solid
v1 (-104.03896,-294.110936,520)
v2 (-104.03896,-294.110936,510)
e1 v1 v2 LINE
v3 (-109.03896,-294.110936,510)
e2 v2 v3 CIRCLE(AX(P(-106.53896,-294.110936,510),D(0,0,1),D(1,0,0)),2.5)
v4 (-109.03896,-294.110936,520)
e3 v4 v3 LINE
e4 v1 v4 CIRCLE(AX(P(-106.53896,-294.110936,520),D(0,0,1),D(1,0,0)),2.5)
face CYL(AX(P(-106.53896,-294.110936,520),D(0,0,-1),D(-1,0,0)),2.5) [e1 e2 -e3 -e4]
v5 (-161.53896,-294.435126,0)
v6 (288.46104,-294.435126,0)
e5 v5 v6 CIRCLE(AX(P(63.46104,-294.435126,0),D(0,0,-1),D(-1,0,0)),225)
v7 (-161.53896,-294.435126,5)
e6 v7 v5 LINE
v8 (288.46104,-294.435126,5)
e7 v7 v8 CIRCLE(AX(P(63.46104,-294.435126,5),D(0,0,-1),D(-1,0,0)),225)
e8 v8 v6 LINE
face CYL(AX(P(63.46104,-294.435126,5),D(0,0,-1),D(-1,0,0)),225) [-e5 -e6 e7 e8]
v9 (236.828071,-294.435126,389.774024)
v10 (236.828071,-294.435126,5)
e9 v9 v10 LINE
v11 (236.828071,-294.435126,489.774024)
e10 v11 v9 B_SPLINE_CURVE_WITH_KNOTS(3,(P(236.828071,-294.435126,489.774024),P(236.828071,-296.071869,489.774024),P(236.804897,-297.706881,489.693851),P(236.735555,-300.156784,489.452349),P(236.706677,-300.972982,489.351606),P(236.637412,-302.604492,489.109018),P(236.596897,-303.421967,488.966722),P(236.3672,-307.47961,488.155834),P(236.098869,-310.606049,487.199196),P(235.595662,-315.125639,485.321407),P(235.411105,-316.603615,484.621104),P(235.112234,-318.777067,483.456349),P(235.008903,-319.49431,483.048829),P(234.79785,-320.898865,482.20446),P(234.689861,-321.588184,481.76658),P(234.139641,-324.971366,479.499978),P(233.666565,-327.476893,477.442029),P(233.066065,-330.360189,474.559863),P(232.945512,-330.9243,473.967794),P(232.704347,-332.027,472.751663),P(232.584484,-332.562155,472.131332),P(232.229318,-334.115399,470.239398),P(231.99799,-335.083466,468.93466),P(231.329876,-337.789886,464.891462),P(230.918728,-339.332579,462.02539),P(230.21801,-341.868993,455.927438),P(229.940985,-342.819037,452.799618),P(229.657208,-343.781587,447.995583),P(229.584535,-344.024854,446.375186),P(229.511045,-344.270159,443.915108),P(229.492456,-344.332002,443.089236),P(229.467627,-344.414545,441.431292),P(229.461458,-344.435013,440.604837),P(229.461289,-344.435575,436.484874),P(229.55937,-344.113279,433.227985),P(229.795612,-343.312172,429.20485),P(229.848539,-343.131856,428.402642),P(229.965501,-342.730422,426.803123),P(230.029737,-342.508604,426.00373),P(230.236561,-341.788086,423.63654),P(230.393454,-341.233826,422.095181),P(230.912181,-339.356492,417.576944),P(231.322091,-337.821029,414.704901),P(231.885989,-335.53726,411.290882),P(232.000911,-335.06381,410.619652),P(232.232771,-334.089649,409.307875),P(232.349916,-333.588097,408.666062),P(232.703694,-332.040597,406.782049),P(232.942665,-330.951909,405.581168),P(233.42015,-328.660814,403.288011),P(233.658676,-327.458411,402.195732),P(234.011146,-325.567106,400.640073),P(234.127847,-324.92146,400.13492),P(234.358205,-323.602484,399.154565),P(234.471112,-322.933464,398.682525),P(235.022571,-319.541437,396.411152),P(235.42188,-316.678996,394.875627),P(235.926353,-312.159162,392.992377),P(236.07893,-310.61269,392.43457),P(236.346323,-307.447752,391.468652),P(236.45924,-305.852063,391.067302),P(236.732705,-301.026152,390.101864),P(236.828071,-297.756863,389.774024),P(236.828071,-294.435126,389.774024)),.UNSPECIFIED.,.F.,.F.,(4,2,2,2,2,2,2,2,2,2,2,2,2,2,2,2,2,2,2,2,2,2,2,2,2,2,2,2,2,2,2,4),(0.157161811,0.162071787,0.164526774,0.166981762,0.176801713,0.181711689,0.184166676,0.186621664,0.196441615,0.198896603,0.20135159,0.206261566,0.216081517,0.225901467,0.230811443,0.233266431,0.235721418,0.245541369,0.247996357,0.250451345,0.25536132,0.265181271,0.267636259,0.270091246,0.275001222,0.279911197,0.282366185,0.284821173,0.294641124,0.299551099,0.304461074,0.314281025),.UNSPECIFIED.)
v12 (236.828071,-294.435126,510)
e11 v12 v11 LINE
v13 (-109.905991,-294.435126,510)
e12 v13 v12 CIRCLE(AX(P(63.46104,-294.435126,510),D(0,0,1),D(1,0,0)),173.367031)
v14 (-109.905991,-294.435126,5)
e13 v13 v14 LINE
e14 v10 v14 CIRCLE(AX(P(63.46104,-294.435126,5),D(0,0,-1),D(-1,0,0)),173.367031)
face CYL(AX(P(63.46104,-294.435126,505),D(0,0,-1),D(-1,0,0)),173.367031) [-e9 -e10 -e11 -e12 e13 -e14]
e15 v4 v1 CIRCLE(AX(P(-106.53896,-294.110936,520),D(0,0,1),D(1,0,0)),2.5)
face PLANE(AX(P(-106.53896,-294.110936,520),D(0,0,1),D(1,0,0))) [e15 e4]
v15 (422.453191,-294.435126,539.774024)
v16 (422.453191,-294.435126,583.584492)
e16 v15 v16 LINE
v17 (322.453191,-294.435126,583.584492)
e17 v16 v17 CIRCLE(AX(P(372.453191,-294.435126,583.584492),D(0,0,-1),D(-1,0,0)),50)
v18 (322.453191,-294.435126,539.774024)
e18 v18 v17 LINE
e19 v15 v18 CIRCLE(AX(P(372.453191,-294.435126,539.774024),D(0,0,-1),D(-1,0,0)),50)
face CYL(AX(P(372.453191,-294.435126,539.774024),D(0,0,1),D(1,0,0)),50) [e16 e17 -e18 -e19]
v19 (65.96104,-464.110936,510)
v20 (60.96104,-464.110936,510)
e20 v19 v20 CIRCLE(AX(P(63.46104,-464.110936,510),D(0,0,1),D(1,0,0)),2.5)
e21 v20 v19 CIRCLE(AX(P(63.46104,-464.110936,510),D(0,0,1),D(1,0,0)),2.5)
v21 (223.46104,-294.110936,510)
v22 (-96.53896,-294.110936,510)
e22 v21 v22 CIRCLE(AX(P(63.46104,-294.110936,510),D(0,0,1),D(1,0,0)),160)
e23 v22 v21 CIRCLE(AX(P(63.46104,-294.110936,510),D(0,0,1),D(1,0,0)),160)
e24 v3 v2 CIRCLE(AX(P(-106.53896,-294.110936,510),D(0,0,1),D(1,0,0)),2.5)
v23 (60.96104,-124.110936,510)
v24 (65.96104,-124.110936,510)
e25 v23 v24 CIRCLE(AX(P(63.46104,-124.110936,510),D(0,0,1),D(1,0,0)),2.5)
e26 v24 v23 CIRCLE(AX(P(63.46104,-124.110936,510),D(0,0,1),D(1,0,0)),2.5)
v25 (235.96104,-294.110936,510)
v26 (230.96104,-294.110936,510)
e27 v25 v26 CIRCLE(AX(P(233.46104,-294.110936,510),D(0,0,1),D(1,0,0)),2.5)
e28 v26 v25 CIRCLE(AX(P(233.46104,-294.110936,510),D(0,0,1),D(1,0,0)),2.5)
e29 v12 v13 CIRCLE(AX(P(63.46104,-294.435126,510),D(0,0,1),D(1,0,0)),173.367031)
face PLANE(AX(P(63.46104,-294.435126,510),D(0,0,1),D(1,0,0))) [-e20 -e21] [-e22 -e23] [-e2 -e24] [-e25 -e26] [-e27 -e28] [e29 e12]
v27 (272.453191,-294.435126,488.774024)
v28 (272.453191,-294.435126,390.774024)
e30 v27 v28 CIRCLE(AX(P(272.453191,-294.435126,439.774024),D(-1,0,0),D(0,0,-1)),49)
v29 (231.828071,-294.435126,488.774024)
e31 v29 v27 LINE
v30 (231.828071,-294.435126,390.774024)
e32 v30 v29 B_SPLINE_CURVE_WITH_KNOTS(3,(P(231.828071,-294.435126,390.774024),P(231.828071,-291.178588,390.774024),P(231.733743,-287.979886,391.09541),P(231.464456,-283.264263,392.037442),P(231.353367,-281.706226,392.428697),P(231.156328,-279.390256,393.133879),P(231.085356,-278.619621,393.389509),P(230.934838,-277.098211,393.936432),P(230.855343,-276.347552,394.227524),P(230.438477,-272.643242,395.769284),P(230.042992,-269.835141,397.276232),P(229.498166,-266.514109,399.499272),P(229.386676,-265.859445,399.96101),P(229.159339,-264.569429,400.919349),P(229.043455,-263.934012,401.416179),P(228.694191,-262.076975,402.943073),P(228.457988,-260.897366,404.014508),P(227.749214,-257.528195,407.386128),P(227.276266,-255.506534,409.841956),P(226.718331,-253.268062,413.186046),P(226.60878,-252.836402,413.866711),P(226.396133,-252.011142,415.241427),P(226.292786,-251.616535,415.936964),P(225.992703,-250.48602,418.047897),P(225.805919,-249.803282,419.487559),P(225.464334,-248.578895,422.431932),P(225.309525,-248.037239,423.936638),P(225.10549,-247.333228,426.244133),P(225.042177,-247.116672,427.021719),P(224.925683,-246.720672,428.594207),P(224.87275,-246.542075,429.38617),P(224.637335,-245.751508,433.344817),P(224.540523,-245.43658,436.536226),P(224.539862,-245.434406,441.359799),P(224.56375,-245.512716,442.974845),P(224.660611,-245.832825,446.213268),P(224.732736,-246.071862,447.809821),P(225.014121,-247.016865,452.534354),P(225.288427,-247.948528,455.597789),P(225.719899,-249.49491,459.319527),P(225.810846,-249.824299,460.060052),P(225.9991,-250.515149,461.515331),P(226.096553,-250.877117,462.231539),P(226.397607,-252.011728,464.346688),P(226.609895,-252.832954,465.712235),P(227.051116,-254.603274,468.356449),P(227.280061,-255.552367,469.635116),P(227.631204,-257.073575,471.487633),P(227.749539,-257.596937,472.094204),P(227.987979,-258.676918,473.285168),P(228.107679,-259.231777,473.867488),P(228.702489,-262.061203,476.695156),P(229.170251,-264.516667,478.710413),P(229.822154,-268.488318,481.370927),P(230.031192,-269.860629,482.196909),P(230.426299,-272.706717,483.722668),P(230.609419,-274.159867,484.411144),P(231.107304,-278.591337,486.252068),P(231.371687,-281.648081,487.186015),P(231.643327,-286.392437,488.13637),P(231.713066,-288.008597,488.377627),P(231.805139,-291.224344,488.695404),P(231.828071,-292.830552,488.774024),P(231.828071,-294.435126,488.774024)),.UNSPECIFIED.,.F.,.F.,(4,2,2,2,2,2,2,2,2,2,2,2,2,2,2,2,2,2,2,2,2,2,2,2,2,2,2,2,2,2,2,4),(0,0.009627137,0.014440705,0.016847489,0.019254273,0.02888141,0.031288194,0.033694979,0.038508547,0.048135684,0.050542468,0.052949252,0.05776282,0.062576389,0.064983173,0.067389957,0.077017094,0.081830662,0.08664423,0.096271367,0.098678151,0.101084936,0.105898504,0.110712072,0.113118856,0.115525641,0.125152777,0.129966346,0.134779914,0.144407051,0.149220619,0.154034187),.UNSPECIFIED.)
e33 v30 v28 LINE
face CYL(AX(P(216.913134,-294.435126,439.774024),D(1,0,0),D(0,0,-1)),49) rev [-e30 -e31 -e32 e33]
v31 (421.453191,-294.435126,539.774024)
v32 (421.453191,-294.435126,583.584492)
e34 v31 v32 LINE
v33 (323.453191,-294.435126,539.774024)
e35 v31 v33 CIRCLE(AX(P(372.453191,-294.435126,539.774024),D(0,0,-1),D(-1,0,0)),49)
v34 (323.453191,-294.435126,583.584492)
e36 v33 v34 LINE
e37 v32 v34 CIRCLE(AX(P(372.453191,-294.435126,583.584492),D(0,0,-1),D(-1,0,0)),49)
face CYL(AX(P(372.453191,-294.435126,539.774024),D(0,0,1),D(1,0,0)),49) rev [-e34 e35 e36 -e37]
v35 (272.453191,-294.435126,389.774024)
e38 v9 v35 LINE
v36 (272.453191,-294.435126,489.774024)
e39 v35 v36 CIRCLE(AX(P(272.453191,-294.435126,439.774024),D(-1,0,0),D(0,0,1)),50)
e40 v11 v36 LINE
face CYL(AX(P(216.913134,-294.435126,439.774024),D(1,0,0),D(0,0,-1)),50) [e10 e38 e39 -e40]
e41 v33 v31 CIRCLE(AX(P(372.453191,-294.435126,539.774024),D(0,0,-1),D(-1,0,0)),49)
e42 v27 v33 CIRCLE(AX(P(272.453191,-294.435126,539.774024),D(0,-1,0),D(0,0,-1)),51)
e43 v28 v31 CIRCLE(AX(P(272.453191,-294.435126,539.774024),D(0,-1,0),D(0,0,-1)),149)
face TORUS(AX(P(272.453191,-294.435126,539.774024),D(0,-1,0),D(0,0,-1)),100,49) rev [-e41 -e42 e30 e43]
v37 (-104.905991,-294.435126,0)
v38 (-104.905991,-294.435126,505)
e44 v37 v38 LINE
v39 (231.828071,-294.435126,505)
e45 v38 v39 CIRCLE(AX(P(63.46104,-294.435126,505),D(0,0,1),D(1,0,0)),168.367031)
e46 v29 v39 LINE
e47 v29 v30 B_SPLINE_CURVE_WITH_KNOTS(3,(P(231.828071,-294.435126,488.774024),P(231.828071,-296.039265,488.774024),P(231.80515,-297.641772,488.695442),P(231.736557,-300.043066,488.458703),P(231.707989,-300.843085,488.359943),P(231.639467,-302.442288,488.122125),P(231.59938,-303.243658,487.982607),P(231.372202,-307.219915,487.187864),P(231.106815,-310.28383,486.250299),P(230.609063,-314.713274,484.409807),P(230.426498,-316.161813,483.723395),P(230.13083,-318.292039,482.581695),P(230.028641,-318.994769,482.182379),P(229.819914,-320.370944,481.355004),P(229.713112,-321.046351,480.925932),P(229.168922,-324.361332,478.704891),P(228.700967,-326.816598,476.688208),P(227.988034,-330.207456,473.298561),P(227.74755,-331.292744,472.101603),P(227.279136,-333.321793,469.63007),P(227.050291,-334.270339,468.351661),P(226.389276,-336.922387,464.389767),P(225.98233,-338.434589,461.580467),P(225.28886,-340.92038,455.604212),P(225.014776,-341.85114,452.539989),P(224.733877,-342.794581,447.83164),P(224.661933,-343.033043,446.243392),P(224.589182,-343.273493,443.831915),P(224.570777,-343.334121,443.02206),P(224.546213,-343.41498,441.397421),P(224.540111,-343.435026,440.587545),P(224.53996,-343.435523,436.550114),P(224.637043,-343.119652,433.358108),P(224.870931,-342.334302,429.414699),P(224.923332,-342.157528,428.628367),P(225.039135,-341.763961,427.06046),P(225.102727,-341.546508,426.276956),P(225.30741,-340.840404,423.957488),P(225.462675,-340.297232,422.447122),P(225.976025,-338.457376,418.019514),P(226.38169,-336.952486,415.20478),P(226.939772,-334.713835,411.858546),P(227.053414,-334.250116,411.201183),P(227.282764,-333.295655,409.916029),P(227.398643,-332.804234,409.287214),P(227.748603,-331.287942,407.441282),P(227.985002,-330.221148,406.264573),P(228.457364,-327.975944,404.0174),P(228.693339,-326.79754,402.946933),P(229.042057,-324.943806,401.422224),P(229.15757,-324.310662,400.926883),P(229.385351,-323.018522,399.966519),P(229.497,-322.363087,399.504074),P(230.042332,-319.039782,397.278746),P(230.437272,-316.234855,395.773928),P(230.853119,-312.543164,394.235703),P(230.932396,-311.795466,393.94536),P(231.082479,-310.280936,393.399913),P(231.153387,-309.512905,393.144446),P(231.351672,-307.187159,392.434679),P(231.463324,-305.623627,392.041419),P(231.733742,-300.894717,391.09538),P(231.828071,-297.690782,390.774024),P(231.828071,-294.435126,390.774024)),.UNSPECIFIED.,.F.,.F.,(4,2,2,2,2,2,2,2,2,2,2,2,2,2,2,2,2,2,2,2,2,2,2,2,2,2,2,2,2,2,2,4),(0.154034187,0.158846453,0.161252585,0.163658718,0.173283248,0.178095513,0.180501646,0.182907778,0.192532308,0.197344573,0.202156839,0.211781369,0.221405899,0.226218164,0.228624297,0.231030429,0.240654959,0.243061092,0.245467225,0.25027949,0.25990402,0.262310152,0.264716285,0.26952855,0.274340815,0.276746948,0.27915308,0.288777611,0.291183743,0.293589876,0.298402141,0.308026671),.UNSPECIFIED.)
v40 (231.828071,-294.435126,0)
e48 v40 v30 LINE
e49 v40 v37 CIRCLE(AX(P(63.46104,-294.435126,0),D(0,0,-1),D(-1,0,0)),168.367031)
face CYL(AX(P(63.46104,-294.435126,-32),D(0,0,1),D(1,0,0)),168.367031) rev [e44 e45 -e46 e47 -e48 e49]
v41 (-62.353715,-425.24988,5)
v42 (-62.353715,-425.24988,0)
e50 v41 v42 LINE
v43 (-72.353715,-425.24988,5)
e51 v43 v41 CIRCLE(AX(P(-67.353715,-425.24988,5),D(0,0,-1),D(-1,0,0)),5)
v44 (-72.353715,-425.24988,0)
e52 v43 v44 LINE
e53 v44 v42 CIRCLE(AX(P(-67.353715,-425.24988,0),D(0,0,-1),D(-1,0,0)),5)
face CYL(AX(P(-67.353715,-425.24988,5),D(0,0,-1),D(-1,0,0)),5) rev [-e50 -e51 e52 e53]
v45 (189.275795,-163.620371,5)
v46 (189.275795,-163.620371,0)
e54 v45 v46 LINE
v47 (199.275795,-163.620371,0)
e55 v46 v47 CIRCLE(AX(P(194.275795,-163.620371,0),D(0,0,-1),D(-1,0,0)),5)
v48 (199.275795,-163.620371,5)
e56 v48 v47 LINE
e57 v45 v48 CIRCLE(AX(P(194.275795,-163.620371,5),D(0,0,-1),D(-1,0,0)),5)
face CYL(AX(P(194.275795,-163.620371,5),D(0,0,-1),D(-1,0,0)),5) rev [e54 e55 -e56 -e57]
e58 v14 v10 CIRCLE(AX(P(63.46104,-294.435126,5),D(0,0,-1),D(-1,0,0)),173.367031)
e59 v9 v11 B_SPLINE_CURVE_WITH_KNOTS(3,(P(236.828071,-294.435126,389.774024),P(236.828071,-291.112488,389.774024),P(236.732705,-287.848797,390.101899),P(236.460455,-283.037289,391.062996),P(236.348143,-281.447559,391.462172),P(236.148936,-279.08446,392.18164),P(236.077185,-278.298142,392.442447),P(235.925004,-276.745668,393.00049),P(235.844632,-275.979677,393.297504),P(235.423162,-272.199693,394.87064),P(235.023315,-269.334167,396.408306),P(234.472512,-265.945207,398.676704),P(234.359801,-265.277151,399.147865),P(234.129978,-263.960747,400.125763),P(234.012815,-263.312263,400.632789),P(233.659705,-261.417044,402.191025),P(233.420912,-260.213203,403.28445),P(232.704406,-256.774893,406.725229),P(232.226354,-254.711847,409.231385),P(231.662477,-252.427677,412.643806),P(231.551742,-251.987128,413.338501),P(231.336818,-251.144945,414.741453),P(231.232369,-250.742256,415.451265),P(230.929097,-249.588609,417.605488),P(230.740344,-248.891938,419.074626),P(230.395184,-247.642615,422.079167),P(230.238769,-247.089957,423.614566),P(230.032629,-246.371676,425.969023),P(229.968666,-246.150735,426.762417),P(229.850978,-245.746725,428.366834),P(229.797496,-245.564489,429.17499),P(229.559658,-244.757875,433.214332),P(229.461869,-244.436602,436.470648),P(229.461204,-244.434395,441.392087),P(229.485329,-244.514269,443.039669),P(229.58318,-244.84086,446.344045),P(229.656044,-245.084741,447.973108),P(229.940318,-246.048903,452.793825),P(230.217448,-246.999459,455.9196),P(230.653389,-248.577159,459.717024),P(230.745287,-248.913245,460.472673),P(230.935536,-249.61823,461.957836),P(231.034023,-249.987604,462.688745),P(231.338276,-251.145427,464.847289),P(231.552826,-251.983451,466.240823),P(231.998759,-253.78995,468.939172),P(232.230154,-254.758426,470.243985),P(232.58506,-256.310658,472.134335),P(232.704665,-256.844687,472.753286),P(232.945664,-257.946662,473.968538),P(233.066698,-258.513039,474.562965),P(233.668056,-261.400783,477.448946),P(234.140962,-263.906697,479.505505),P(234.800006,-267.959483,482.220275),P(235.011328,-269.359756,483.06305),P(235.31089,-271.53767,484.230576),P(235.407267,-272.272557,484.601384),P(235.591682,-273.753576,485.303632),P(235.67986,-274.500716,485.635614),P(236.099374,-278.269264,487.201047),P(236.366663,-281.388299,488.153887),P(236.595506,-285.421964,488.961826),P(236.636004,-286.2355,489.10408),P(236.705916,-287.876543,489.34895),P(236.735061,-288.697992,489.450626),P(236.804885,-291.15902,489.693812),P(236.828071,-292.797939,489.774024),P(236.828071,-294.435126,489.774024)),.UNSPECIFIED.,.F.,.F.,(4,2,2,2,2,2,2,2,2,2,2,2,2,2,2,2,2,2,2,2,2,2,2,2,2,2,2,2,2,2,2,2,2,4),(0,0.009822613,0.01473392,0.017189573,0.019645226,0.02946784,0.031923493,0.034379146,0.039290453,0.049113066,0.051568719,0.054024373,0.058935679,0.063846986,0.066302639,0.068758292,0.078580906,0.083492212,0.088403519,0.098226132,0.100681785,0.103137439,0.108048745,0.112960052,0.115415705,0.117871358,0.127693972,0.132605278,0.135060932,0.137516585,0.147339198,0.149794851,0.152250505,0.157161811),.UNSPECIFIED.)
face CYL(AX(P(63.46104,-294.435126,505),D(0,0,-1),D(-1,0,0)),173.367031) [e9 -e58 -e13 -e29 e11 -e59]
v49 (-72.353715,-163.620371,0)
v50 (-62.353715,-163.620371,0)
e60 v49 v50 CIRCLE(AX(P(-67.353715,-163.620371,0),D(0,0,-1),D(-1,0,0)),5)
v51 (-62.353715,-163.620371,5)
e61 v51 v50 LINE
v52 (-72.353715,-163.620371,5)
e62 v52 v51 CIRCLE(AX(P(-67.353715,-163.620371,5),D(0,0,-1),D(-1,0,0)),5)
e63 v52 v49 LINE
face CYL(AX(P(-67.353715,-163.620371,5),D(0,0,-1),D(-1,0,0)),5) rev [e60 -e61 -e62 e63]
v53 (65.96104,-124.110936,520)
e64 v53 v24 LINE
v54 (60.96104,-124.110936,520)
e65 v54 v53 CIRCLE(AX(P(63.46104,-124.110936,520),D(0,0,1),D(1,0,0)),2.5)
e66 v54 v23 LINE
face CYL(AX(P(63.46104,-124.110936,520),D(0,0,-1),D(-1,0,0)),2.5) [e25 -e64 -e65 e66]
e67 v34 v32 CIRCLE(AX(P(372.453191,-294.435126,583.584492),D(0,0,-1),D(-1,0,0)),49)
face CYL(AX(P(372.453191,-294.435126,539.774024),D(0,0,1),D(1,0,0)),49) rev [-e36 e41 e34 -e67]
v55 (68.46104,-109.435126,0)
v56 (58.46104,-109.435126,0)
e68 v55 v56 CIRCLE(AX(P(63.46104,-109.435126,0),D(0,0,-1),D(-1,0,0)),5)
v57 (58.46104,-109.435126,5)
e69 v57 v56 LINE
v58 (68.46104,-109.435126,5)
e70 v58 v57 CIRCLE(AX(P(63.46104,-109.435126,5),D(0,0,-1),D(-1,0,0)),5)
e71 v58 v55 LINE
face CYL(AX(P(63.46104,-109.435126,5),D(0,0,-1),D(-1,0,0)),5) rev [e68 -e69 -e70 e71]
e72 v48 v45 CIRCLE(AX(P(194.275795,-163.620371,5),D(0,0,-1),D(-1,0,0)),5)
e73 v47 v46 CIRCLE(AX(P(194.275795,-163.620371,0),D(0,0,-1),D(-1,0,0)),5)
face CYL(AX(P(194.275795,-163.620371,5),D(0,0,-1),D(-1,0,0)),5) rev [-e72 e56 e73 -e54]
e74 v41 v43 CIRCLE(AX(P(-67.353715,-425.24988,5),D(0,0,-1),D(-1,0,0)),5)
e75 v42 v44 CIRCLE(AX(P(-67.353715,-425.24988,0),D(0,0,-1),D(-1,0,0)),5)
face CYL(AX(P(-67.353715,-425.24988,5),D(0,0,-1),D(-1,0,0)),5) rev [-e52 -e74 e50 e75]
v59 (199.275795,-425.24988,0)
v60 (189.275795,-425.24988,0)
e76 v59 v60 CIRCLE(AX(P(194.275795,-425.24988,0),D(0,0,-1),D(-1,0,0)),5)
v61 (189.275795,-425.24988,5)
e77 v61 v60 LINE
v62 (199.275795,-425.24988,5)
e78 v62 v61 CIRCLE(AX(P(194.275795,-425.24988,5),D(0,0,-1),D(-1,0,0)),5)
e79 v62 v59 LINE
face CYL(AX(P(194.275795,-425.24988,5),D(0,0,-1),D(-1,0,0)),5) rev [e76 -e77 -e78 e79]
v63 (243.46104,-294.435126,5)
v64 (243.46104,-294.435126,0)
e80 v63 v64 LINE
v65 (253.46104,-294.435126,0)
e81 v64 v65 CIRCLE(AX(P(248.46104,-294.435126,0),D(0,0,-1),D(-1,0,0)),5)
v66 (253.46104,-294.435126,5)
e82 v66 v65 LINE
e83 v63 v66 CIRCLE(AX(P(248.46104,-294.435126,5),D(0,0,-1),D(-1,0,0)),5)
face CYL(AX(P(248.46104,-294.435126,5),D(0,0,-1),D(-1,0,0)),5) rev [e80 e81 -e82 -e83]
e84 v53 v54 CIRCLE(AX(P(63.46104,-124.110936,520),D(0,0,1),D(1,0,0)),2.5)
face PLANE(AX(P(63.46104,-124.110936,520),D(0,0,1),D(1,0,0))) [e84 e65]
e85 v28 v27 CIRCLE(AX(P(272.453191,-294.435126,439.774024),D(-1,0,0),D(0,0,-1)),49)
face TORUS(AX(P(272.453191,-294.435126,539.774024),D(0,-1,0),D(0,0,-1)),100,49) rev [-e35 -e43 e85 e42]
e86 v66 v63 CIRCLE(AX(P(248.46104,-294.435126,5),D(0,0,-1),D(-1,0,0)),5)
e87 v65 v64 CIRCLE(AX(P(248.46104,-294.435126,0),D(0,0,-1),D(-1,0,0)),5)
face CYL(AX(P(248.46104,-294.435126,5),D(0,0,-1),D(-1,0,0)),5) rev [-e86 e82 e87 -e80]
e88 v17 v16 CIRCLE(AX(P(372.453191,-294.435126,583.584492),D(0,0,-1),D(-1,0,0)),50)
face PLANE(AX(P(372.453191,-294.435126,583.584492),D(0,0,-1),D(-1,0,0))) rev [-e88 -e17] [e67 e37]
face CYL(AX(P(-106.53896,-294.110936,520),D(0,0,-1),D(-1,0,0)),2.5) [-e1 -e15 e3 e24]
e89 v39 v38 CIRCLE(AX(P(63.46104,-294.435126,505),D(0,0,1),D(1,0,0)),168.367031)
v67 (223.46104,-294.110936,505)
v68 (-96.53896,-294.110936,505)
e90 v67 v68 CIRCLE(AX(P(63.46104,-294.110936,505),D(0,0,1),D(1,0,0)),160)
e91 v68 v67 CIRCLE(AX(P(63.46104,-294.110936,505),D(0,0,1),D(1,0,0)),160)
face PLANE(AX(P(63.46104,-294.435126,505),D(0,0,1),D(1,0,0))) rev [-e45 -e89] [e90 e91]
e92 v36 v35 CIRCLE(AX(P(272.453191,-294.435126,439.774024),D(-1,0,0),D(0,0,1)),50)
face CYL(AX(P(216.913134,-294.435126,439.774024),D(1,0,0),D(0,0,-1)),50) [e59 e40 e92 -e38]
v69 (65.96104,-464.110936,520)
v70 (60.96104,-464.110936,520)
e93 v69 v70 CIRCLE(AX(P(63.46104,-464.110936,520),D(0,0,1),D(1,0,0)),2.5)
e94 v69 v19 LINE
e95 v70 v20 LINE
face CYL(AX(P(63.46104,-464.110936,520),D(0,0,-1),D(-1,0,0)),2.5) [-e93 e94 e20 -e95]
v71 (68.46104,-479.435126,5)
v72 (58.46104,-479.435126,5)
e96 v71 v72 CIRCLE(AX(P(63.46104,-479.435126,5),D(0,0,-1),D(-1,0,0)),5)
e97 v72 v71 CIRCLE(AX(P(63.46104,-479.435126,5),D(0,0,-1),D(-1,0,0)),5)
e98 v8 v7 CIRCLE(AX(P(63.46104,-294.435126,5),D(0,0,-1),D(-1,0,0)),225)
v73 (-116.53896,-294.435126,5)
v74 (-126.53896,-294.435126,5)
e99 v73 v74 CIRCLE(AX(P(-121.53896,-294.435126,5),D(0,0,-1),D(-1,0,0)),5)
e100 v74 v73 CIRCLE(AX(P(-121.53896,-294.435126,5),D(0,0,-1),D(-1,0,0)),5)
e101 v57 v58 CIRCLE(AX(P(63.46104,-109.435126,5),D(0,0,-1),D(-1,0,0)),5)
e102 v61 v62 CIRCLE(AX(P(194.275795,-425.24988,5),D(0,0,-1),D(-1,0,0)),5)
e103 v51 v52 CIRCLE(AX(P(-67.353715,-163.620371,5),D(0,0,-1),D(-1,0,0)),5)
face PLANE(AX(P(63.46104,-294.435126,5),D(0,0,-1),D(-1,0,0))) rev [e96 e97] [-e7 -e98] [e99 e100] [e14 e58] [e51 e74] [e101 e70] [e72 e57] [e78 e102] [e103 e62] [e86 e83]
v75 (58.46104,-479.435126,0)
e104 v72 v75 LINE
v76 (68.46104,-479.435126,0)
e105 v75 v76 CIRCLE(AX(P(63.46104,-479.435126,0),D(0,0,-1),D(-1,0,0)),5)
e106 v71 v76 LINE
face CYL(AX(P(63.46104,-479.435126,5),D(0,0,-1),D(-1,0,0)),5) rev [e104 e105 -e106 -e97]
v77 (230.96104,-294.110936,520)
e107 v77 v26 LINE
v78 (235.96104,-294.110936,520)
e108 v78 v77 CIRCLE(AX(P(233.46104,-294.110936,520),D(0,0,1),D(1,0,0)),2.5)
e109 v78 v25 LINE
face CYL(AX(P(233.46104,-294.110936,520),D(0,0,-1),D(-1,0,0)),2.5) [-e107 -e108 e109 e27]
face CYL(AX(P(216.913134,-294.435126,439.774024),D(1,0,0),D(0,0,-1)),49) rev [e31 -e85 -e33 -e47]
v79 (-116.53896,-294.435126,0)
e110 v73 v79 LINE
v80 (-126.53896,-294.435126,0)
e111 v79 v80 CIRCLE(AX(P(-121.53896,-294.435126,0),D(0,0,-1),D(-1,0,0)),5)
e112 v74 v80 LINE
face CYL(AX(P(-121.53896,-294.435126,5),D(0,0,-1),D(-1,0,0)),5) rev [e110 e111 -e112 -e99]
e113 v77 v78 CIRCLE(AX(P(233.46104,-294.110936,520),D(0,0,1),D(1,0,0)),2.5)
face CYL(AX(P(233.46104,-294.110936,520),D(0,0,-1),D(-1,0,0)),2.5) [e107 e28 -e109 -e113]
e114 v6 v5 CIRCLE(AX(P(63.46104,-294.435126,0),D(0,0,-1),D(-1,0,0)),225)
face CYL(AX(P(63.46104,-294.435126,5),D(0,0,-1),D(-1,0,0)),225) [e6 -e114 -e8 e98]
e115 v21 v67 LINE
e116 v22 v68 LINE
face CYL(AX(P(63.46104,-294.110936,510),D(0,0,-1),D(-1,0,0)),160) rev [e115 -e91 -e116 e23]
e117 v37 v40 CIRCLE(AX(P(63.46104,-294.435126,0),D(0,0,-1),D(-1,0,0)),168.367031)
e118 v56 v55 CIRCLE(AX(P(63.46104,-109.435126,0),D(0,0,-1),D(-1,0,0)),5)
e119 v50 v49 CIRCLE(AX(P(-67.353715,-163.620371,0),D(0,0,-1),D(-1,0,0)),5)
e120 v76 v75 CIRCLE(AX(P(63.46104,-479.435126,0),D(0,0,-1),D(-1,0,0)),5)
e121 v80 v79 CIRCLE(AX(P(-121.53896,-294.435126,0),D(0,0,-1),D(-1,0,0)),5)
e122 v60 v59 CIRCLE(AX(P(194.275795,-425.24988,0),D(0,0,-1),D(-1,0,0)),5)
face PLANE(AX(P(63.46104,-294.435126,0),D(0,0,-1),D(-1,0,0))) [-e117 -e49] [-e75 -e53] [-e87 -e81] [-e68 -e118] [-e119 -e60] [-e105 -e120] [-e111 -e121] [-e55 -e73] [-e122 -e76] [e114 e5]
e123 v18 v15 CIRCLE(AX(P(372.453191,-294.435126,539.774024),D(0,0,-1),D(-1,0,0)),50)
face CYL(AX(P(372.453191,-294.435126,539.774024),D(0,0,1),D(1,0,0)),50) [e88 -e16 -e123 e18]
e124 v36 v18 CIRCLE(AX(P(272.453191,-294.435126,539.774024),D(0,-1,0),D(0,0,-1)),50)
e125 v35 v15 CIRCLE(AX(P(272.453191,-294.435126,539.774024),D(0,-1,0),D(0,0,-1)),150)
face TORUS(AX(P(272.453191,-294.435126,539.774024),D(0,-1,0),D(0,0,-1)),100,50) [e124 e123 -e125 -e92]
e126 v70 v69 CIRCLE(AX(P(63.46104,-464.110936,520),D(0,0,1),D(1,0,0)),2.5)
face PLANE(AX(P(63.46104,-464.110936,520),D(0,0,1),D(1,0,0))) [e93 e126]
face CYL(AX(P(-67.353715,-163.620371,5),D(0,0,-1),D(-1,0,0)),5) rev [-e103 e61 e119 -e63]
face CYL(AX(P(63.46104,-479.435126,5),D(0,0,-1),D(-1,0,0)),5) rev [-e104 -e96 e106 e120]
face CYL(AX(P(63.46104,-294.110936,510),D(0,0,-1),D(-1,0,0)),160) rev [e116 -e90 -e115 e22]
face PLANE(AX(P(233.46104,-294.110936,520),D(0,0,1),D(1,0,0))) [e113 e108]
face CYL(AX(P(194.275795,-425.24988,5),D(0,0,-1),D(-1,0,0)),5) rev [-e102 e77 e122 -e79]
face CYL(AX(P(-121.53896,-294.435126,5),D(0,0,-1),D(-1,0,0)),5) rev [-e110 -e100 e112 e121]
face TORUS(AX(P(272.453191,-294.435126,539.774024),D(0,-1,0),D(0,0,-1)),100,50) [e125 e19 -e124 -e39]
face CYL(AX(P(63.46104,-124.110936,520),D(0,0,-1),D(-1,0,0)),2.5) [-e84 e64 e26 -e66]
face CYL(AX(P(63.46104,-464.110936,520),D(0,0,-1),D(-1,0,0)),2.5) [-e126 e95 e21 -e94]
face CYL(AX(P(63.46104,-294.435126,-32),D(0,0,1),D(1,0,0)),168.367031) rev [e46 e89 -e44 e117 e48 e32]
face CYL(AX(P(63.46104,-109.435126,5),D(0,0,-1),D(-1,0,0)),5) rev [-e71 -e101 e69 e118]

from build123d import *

# Parameters (mm, degrees)
SKETCH2_R               = 173.367031435
SKETCH2_R_2             = 164.023575254
BOSS_EXTRUDE2_DEPTH     = 500
SKETCH3_R               = 173.367031435
SKETCH3_R_2             = 164.023575254
BOSS_EXTRUDE3_DEPTH     = 5
SWEEP_THIN1_PROFILE_R   = 50
SWEEP_THIN1_PROFILE_R_2 = 49
CUT_EXTRUDE1_START      = -37
SKETCH41_R              = 49
CUT_EXTRUDE1_DEPTH      = 37
SKETCH28_R              = 168.367031435
CUT_EXTRUDE2_DEPTH      = 537
BOSS_EXTRUDE4_START     = -5
SKETCH43_R              = 225
SKETCH43_R_2            = 5
SKETCH43_R_3            = 168.367031435
BOSS_EXTRUDE4_DEPTH     = 5
SKETCH44_R              = 173.367031435
SKETCH44_R_2            = 160
BOSS_EXTRUDE5_DEPTH     = 5
SKETCH47_R              = 2.5
BOSS_EXTRUDE6_DEPTH     = 10


with BuildPart() as part:
    # Sketch2 → Boss-Extrude2 (new body)
    with BuildSketch(Plane.XY.offset(5)):
        with Locations((63.461039989, -294.435125763)):
            Circle(SKETCH2_R)
        with Locations((63.461039989, -294.435125763)):
            Circle(SKETCH2_R_2, mode=Mode.SUBTRACT)
    extrude(amount=BOSS_EXTRUDE2_DEPTH)

    # Sketch3 → Boss-Extrude3 (add)
    with BuildSketch(Plane(origin=(0, 0, 0), x_dir=(-1, 0, 0), z_dir=(0, 0, -1))):
        with Locations((-63.461039989, -294.435125763)):
            Circle(SKETCH3_R)
        with Locations((-63.461039989, -294.435125763)):
            Circle(SKETCH3_R_2, mode=Mode.SUBTRACT)
    extrude(amount=-BOSS_EXTRUDE3_DEPTH)

    # Sweep-Thin1: sweep along a path in Sketch4
    with BuildLine(Plane(origin=(0, -294.435125763, 0), x_dir=(0, 0, -1), z_dir=(0, -1, 0))) as sweep_thin1_path:
        Line((-439.774024061, 216.913134458), (-439.774024061, 272.453191162))
        ThreePointArc((-439.774024061, 272.453191162), (-469.063345943, 343.163869281), (-539.774024061, 372.453191162))
        Line((-539.774024061, 372.453191162), (-583.584491555, 372.453191162))
    # Sweep-Thin1 profile (on start of the path) → Sweep-Thin1 (sweep)
    with BuildSketch(Plane(origin=(216.913134458, -294.435125763, 439.774024061), x_dir=(0, 0, 1), z_dir=(1, 0, 0))):
        Circle(SWEEP_THIN1_PROFILE_R)
        Circle(SWEEP_THIN1_PROFILE_R_2, mode=Mode.SUBTRACT)
    sweep(path=sweep_thin1_path.line)

    # Sketch41 → Cut-Extrude1 (cut)
    with BuildSketch(Plane.ZY.offset(-216.913134458).offset(CUT_EXTRUDE1_START)):
        with Locations(Location((439.774024061, -294.435125763, 0), (0, 0, 180))):
            Circle(SKETCH41_R)
    extrude(amount=CUT_EXTRUDE1_DEPTH, mode=Mode.SUBTRACT)

    # Sketch28 → Cut-Extrude2 (cut)
    with BuildSketch(Plane.XY.offset(505)):
        with Locations((63.461039989, -294.435125763)):
            Circle(SKETCH28_R)
    extrude(amount=-CUT_EXTRUDE2_DEPTH, mode=Mode.SUBTRACT)

    # Sketch43 → Boss-Extrude4 (add)
    with BuildSketch(Plane(origin=(0, 0, 0), x_dir=(-1, 0, 0), z_dir=(0, 0, -1)).offset(BOSS_EXTRUDE4_START)):
        with Locations((-63.461039989, -294.435125763)):
            Circle(SKETCH43_R)
        with Locations((-63.461039989, -109.435125763)):
            Circle(SKETCH43_R_2, mode=Mode.SUBTRACT)
        with Locations((67.353714531, -163.620371244)):
            Circle(SKETCH43_R_2, mode=Mode.SUBTRACT)
        with Locations((121.538960011, -294.435125763)):
            Circle(SKETCH43_R_2, mode=Mode.SUBTRACT)
        with Locations((67.353714531, -425.249880283)):
            Circle(SKETCH43_R_2, mode=Mode.SUBTRACT)
        with Locations((-63.461039989, -479.435125763)):
            Circle(SKETCH43_R_2, mode=Mode.SUBTRACT)
        with Locations((-194.275794508, -425.249880283)):
            Circle(SKETCH43_R_2, mode=Mode.SUBTRACT)
        with Locations((-248.461039989, -294.435125763)):
            Circle(SKETCH43_R_2, mode=Mode.SUBTRACT)
        with Locations((-194.275794508, -163.620371244)):
            Circle(SKETCH43_R_2, mode=Mode.SUBTRACT)
        with Locations(Location((-63.461039989, -294.435125763, 0), (0, 0, 180))):
            Circle(SKETCH43_R_3, mode=Mode.SUBTRACT)
    extrude(amount=BOSS_EXTRUDE4_DEPTH)

    # Sketch44 → Boss-Extrude5 (add)
    with BuildSketch(Plane.XY.offset(505)):
        with Locations(Location((63.461039989, -294.435125763, 0), (0, 0, 180))):
            Circle(SKETCH44_R)
        with Locations((63.461039989, -294.110936305)):
            Circle(SKETCH44_R_2, mode=Mode.SUBTRACT)
    extrude(amount=BOSS_EXTRUDE5_DEPTH)

    # Sketch47 → Boss-Extrude6 (add)
    with BuildSketch(Plane.XY.offset(510)):
        with Locations((-106.538960011, -294.110936305)):
            Circle(SKETCH47_R)
        with Locations((63.461039989, -124.110936305)):
            Circle(SKETCH47_R)
        with Locations((233.461039989, -294.110936305)):
            Circle(SKETCH47_R)
        with Locations((63.461039989, -464.110936305)):
            Circle(SKETCH47_R)
    extrude(amount=BOSS_EXTRUDE6_DEPTH)


solid = part.part
